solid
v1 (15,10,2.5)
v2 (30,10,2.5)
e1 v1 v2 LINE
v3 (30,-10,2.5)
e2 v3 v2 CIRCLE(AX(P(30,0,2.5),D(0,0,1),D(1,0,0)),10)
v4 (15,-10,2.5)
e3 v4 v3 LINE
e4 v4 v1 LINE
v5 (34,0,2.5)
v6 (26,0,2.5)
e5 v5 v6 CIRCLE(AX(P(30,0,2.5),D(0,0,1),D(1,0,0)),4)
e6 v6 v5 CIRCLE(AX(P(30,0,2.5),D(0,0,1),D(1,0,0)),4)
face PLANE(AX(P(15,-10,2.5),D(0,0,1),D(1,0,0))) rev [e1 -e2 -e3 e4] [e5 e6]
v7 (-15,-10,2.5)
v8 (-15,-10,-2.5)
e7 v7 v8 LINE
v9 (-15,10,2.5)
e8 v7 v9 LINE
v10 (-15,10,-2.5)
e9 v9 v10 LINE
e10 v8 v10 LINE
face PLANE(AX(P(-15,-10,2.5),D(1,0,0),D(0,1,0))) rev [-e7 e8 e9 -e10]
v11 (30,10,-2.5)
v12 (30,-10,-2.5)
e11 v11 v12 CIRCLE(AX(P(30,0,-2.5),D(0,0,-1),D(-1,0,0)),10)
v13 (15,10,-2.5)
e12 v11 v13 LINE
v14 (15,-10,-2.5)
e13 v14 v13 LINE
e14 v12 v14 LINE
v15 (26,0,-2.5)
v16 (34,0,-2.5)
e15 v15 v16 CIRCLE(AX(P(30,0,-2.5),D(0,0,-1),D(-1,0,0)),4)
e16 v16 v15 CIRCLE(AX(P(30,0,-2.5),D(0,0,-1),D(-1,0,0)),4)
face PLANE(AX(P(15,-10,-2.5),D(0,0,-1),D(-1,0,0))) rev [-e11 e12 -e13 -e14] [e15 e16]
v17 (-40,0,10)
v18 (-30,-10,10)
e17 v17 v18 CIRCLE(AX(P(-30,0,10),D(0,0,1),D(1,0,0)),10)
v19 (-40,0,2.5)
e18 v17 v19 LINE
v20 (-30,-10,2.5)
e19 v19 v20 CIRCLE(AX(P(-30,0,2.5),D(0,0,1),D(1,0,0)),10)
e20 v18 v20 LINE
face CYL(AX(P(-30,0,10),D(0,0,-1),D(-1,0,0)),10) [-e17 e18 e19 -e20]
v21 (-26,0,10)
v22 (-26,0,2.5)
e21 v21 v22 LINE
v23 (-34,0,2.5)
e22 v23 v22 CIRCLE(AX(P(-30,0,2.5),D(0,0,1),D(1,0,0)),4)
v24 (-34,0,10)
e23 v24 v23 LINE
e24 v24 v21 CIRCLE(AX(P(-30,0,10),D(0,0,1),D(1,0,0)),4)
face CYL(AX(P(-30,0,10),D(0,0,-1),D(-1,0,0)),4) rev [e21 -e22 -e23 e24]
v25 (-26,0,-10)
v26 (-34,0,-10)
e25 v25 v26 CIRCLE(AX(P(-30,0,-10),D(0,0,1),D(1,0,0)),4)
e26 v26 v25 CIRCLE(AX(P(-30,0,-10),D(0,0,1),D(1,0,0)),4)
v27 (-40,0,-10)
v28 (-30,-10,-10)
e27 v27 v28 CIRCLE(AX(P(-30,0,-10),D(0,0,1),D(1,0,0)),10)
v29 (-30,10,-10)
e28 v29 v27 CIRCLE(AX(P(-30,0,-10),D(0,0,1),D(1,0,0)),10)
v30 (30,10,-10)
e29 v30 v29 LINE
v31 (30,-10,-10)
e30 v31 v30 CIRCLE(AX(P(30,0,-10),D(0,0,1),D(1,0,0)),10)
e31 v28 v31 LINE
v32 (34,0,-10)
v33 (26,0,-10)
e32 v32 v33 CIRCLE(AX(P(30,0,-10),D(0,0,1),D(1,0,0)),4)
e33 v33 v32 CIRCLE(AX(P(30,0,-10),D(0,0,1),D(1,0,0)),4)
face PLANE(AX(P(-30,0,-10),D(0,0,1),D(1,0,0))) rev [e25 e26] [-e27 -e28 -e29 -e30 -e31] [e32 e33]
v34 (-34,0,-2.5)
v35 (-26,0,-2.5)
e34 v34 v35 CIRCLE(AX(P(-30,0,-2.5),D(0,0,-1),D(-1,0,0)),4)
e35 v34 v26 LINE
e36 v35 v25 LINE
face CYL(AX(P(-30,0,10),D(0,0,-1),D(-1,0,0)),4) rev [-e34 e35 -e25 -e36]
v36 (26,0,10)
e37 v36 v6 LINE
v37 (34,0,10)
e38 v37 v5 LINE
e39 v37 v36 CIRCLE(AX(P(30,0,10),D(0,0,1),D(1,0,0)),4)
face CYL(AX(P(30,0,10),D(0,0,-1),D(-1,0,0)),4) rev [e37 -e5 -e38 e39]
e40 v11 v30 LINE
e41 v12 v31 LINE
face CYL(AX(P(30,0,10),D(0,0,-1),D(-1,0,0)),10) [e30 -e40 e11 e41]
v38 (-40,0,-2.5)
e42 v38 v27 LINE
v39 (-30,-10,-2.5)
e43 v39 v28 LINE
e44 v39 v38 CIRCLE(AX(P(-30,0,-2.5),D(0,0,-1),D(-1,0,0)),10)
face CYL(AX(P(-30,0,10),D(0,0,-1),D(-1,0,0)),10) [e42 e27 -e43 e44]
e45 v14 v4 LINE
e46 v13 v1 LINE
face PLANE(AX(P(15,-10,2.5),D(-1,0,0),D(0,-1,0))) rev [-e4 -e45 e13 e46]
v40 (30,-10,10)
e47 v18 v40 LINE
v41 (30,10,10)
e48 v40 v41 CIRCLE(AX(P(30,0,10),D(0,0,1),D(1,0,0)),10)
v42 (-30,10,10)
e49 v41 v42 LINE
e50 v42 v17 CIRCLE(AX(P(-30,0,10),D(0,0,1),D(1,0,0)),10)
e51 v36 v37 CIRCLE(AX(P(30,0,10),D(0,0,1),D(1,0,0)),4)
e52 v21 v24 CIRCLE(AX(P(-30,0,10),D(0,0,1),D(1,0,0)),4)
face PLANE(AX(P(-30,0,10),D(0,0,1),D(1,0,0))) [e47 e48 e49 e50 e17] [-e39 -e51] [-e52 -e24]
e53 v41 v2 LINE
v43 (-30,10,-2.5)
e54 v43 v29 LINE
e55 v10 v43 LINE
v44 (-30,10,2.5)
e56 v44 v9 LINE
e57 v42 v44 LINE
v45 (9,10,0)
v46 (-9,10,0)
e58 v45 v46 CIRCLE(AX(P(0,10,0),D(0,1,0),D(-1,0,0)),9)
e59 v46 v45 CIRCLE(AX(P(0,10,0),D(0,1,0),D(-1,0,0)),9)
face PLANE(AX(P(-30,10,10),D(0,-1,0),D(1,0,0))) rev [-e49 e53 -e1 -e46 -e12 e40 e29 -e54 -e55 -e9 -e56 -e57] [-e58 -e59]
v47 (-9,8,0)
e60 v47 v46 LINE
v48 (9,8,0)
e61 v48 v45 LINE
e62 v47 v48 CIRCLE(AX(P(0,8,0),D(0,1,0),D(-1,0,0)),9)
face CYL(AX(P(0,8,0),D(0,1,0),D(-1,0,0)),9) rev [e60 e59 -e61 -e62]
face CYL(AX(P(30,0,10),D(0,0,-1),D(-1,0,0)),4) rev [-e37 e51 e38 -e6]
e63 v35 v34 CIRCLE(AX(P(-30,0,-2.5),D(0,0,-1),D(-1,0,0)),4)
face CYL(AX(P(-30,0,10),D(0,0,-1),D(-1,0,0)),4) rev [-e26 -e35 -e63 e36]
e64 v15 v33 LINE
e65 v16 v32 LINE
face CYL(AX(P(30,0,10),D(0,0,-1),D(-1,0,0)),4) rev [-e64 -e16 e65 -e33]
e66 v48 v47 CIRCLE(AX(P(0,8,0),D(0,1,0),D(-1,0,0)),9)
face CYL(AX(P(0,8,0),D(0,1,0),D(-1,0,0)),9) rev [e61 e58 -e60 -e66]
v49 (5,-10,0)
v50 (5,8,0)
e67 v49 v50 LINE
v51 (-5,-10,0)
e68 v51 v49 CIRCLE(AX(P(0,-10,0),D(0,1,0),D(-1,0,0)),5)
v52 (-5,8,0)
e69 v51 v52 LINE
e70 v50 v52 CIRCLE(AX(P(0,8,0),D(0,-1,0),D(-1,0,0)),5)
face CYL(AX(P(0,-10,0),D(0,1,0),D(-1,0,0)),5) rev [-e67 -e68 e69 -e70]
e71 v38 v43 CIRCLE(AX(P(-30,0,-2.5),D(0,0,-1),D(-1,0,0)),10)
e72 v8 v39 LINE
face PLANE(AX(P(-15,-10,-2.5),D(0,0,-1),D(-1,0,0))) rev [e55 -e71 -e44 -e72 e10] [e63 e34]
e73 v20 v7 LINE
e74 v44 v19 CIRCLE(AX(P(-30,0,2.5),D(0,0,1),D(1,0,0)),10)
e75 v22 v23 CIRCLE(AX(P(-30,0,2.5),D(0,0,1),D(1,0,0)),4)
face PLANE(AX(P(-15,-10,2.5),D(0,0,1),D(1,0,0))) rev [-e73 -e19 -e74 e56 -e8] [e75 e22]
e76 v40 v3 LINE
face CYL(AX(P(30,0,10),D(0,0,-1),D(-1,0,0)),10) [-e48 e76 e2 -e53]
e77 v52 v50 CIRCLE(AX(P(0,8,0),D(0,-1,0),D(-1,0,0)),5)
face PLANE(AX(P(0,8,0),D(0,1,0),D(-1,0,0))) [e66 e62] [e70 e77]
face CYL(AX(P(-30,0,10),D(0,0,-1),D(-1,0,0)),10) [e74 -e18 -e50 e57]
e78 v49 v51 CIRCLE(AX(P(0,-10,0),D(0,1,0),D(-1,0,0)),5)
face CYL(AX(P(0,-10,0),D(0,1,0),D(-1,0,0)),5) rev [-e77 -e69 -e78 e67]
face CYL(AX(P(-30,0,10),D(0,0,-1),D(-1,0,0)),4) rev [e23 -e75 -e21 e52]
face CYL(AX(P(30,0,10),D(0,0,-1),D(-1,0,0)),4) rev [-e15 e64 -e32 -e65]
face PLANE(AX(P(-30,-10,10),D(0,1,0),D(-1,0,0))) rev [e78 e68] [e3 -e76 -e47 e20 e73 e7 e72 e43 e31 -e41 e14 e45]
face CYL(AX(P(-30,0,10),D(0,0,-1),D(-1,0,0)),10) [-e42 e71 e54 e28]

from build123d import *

# Parameters (mm, degrees)
LINK_PROFILE_SKETCH_R           = 4
LINK_BODY_DEPTH                 = 10
END_CLEVIS_SLOTS_5MM_DEPTH      = 46.82575695
END_CLEVIS_SLOTS_5MM_DEPTH_BACK = 46.82575695
END_SLOTS_SKETCH_W              = 25
END_SLOTS_SKETCH_H              = 5
CENTRE_HOLE_10_DEPTH            = 46.82575695
CENTRE_HOLE_10_DEPTH_BACK       = 46.82575695
CENTRE_HOLE_SKETCH_R            = 5
COUNTERBORE_SKETCH_R            = 9
COUNTERBORE_18X2_DEPTH          = 2


with BuildPart() as part:
    # Link Profile Sketch → Link Body (new, symmetric)
    with BuildSketch(Plane.XY):
        with BuildLine():
            Line((-30, 10), (30, 10))
            ThreePointArc((30, 10), (40, 0), (30, -10))
            Line((30, -10), (-30, -10))
            ThreePointArc((-30, -10), (-40, 0), (-30, 10))
        make_face()
        with Locations((-30, 0)):
            Circle(LINK_PROFILE_SKETCH_R, mode=Mode.SUBTRACT)
        with Locations((30, 0)):
            Circle(LINK_PROFILE_SKETCH_R, mode=Mode.SUBTRACT)
    extrude(amount=LINK_BODY_DEPTH, both=True)

    # End Slots Sketch → End Clevis Slots 5mm (cut, two sides: drawn at the far end of the back side and taken through both)
    with BuildSketch(Plane(origin=(0, 10, 0), x_dir=(1, 0, 0), z_dir=(0, 1, 0)).offset(-END_CLEVIS_SLOTS_5MM_DEPTH_BACK)):
        with Locations((-27.5, 0)):
            Rectangle(END_SLOTS_SKETCH_W, END_SLOTS_SKETCH_H)
        with Locations((27.5, 0)):
            Rectangle(END_SLOTS_SKETCH_W, END_SLOTS_SKETCH_H)
    extrude(amount=END_CLEVIS_SLOTS_5MM_DEPTH + END_CLEVIS_SLOTS_5MM_DEPTH_BACK, mode=Mode.SUBTRACT)

    # Centre Hole Sketch → Centre Hole Ø10 (cut, two sides: drawn at the far end of the back side and taken through both)
    with BuildSketch(Plane(origin=(0, 10, 0), x_dir=(1, 0, 0), z_dir=(0, 1, 0)).offset(-CENTRE_HOLE_10_DEPTH_BACK)):
        with Locations(Location((0, 0, 0), (0, 0, 180))):
            Circle(CENTRE_HOLE_SKETCH_R)
    extrude(amount=CENTRE_HOLE_10_DEPTH + CENTRE_HOLE_10_DEPTH_BACK, mode=Mode.SUBTRACT)

    # Counterbore Sketch → Counterbore Ø18x2 (cut)
    with BuildSketch(Plane(origin=(0, 10, 0), x_dir=(1, 0, 0), z_dir=(0, 1, 0))):
        with Locations(Location((0, 0, 0), (0, 0, 180))):
            Circle(COUNTERBORE_SKETCH_R)
    extrude(amount=-COUNTERBORE_18X2_DEPTH, mode=Mode.SUBTRACT)


solid = part.part
